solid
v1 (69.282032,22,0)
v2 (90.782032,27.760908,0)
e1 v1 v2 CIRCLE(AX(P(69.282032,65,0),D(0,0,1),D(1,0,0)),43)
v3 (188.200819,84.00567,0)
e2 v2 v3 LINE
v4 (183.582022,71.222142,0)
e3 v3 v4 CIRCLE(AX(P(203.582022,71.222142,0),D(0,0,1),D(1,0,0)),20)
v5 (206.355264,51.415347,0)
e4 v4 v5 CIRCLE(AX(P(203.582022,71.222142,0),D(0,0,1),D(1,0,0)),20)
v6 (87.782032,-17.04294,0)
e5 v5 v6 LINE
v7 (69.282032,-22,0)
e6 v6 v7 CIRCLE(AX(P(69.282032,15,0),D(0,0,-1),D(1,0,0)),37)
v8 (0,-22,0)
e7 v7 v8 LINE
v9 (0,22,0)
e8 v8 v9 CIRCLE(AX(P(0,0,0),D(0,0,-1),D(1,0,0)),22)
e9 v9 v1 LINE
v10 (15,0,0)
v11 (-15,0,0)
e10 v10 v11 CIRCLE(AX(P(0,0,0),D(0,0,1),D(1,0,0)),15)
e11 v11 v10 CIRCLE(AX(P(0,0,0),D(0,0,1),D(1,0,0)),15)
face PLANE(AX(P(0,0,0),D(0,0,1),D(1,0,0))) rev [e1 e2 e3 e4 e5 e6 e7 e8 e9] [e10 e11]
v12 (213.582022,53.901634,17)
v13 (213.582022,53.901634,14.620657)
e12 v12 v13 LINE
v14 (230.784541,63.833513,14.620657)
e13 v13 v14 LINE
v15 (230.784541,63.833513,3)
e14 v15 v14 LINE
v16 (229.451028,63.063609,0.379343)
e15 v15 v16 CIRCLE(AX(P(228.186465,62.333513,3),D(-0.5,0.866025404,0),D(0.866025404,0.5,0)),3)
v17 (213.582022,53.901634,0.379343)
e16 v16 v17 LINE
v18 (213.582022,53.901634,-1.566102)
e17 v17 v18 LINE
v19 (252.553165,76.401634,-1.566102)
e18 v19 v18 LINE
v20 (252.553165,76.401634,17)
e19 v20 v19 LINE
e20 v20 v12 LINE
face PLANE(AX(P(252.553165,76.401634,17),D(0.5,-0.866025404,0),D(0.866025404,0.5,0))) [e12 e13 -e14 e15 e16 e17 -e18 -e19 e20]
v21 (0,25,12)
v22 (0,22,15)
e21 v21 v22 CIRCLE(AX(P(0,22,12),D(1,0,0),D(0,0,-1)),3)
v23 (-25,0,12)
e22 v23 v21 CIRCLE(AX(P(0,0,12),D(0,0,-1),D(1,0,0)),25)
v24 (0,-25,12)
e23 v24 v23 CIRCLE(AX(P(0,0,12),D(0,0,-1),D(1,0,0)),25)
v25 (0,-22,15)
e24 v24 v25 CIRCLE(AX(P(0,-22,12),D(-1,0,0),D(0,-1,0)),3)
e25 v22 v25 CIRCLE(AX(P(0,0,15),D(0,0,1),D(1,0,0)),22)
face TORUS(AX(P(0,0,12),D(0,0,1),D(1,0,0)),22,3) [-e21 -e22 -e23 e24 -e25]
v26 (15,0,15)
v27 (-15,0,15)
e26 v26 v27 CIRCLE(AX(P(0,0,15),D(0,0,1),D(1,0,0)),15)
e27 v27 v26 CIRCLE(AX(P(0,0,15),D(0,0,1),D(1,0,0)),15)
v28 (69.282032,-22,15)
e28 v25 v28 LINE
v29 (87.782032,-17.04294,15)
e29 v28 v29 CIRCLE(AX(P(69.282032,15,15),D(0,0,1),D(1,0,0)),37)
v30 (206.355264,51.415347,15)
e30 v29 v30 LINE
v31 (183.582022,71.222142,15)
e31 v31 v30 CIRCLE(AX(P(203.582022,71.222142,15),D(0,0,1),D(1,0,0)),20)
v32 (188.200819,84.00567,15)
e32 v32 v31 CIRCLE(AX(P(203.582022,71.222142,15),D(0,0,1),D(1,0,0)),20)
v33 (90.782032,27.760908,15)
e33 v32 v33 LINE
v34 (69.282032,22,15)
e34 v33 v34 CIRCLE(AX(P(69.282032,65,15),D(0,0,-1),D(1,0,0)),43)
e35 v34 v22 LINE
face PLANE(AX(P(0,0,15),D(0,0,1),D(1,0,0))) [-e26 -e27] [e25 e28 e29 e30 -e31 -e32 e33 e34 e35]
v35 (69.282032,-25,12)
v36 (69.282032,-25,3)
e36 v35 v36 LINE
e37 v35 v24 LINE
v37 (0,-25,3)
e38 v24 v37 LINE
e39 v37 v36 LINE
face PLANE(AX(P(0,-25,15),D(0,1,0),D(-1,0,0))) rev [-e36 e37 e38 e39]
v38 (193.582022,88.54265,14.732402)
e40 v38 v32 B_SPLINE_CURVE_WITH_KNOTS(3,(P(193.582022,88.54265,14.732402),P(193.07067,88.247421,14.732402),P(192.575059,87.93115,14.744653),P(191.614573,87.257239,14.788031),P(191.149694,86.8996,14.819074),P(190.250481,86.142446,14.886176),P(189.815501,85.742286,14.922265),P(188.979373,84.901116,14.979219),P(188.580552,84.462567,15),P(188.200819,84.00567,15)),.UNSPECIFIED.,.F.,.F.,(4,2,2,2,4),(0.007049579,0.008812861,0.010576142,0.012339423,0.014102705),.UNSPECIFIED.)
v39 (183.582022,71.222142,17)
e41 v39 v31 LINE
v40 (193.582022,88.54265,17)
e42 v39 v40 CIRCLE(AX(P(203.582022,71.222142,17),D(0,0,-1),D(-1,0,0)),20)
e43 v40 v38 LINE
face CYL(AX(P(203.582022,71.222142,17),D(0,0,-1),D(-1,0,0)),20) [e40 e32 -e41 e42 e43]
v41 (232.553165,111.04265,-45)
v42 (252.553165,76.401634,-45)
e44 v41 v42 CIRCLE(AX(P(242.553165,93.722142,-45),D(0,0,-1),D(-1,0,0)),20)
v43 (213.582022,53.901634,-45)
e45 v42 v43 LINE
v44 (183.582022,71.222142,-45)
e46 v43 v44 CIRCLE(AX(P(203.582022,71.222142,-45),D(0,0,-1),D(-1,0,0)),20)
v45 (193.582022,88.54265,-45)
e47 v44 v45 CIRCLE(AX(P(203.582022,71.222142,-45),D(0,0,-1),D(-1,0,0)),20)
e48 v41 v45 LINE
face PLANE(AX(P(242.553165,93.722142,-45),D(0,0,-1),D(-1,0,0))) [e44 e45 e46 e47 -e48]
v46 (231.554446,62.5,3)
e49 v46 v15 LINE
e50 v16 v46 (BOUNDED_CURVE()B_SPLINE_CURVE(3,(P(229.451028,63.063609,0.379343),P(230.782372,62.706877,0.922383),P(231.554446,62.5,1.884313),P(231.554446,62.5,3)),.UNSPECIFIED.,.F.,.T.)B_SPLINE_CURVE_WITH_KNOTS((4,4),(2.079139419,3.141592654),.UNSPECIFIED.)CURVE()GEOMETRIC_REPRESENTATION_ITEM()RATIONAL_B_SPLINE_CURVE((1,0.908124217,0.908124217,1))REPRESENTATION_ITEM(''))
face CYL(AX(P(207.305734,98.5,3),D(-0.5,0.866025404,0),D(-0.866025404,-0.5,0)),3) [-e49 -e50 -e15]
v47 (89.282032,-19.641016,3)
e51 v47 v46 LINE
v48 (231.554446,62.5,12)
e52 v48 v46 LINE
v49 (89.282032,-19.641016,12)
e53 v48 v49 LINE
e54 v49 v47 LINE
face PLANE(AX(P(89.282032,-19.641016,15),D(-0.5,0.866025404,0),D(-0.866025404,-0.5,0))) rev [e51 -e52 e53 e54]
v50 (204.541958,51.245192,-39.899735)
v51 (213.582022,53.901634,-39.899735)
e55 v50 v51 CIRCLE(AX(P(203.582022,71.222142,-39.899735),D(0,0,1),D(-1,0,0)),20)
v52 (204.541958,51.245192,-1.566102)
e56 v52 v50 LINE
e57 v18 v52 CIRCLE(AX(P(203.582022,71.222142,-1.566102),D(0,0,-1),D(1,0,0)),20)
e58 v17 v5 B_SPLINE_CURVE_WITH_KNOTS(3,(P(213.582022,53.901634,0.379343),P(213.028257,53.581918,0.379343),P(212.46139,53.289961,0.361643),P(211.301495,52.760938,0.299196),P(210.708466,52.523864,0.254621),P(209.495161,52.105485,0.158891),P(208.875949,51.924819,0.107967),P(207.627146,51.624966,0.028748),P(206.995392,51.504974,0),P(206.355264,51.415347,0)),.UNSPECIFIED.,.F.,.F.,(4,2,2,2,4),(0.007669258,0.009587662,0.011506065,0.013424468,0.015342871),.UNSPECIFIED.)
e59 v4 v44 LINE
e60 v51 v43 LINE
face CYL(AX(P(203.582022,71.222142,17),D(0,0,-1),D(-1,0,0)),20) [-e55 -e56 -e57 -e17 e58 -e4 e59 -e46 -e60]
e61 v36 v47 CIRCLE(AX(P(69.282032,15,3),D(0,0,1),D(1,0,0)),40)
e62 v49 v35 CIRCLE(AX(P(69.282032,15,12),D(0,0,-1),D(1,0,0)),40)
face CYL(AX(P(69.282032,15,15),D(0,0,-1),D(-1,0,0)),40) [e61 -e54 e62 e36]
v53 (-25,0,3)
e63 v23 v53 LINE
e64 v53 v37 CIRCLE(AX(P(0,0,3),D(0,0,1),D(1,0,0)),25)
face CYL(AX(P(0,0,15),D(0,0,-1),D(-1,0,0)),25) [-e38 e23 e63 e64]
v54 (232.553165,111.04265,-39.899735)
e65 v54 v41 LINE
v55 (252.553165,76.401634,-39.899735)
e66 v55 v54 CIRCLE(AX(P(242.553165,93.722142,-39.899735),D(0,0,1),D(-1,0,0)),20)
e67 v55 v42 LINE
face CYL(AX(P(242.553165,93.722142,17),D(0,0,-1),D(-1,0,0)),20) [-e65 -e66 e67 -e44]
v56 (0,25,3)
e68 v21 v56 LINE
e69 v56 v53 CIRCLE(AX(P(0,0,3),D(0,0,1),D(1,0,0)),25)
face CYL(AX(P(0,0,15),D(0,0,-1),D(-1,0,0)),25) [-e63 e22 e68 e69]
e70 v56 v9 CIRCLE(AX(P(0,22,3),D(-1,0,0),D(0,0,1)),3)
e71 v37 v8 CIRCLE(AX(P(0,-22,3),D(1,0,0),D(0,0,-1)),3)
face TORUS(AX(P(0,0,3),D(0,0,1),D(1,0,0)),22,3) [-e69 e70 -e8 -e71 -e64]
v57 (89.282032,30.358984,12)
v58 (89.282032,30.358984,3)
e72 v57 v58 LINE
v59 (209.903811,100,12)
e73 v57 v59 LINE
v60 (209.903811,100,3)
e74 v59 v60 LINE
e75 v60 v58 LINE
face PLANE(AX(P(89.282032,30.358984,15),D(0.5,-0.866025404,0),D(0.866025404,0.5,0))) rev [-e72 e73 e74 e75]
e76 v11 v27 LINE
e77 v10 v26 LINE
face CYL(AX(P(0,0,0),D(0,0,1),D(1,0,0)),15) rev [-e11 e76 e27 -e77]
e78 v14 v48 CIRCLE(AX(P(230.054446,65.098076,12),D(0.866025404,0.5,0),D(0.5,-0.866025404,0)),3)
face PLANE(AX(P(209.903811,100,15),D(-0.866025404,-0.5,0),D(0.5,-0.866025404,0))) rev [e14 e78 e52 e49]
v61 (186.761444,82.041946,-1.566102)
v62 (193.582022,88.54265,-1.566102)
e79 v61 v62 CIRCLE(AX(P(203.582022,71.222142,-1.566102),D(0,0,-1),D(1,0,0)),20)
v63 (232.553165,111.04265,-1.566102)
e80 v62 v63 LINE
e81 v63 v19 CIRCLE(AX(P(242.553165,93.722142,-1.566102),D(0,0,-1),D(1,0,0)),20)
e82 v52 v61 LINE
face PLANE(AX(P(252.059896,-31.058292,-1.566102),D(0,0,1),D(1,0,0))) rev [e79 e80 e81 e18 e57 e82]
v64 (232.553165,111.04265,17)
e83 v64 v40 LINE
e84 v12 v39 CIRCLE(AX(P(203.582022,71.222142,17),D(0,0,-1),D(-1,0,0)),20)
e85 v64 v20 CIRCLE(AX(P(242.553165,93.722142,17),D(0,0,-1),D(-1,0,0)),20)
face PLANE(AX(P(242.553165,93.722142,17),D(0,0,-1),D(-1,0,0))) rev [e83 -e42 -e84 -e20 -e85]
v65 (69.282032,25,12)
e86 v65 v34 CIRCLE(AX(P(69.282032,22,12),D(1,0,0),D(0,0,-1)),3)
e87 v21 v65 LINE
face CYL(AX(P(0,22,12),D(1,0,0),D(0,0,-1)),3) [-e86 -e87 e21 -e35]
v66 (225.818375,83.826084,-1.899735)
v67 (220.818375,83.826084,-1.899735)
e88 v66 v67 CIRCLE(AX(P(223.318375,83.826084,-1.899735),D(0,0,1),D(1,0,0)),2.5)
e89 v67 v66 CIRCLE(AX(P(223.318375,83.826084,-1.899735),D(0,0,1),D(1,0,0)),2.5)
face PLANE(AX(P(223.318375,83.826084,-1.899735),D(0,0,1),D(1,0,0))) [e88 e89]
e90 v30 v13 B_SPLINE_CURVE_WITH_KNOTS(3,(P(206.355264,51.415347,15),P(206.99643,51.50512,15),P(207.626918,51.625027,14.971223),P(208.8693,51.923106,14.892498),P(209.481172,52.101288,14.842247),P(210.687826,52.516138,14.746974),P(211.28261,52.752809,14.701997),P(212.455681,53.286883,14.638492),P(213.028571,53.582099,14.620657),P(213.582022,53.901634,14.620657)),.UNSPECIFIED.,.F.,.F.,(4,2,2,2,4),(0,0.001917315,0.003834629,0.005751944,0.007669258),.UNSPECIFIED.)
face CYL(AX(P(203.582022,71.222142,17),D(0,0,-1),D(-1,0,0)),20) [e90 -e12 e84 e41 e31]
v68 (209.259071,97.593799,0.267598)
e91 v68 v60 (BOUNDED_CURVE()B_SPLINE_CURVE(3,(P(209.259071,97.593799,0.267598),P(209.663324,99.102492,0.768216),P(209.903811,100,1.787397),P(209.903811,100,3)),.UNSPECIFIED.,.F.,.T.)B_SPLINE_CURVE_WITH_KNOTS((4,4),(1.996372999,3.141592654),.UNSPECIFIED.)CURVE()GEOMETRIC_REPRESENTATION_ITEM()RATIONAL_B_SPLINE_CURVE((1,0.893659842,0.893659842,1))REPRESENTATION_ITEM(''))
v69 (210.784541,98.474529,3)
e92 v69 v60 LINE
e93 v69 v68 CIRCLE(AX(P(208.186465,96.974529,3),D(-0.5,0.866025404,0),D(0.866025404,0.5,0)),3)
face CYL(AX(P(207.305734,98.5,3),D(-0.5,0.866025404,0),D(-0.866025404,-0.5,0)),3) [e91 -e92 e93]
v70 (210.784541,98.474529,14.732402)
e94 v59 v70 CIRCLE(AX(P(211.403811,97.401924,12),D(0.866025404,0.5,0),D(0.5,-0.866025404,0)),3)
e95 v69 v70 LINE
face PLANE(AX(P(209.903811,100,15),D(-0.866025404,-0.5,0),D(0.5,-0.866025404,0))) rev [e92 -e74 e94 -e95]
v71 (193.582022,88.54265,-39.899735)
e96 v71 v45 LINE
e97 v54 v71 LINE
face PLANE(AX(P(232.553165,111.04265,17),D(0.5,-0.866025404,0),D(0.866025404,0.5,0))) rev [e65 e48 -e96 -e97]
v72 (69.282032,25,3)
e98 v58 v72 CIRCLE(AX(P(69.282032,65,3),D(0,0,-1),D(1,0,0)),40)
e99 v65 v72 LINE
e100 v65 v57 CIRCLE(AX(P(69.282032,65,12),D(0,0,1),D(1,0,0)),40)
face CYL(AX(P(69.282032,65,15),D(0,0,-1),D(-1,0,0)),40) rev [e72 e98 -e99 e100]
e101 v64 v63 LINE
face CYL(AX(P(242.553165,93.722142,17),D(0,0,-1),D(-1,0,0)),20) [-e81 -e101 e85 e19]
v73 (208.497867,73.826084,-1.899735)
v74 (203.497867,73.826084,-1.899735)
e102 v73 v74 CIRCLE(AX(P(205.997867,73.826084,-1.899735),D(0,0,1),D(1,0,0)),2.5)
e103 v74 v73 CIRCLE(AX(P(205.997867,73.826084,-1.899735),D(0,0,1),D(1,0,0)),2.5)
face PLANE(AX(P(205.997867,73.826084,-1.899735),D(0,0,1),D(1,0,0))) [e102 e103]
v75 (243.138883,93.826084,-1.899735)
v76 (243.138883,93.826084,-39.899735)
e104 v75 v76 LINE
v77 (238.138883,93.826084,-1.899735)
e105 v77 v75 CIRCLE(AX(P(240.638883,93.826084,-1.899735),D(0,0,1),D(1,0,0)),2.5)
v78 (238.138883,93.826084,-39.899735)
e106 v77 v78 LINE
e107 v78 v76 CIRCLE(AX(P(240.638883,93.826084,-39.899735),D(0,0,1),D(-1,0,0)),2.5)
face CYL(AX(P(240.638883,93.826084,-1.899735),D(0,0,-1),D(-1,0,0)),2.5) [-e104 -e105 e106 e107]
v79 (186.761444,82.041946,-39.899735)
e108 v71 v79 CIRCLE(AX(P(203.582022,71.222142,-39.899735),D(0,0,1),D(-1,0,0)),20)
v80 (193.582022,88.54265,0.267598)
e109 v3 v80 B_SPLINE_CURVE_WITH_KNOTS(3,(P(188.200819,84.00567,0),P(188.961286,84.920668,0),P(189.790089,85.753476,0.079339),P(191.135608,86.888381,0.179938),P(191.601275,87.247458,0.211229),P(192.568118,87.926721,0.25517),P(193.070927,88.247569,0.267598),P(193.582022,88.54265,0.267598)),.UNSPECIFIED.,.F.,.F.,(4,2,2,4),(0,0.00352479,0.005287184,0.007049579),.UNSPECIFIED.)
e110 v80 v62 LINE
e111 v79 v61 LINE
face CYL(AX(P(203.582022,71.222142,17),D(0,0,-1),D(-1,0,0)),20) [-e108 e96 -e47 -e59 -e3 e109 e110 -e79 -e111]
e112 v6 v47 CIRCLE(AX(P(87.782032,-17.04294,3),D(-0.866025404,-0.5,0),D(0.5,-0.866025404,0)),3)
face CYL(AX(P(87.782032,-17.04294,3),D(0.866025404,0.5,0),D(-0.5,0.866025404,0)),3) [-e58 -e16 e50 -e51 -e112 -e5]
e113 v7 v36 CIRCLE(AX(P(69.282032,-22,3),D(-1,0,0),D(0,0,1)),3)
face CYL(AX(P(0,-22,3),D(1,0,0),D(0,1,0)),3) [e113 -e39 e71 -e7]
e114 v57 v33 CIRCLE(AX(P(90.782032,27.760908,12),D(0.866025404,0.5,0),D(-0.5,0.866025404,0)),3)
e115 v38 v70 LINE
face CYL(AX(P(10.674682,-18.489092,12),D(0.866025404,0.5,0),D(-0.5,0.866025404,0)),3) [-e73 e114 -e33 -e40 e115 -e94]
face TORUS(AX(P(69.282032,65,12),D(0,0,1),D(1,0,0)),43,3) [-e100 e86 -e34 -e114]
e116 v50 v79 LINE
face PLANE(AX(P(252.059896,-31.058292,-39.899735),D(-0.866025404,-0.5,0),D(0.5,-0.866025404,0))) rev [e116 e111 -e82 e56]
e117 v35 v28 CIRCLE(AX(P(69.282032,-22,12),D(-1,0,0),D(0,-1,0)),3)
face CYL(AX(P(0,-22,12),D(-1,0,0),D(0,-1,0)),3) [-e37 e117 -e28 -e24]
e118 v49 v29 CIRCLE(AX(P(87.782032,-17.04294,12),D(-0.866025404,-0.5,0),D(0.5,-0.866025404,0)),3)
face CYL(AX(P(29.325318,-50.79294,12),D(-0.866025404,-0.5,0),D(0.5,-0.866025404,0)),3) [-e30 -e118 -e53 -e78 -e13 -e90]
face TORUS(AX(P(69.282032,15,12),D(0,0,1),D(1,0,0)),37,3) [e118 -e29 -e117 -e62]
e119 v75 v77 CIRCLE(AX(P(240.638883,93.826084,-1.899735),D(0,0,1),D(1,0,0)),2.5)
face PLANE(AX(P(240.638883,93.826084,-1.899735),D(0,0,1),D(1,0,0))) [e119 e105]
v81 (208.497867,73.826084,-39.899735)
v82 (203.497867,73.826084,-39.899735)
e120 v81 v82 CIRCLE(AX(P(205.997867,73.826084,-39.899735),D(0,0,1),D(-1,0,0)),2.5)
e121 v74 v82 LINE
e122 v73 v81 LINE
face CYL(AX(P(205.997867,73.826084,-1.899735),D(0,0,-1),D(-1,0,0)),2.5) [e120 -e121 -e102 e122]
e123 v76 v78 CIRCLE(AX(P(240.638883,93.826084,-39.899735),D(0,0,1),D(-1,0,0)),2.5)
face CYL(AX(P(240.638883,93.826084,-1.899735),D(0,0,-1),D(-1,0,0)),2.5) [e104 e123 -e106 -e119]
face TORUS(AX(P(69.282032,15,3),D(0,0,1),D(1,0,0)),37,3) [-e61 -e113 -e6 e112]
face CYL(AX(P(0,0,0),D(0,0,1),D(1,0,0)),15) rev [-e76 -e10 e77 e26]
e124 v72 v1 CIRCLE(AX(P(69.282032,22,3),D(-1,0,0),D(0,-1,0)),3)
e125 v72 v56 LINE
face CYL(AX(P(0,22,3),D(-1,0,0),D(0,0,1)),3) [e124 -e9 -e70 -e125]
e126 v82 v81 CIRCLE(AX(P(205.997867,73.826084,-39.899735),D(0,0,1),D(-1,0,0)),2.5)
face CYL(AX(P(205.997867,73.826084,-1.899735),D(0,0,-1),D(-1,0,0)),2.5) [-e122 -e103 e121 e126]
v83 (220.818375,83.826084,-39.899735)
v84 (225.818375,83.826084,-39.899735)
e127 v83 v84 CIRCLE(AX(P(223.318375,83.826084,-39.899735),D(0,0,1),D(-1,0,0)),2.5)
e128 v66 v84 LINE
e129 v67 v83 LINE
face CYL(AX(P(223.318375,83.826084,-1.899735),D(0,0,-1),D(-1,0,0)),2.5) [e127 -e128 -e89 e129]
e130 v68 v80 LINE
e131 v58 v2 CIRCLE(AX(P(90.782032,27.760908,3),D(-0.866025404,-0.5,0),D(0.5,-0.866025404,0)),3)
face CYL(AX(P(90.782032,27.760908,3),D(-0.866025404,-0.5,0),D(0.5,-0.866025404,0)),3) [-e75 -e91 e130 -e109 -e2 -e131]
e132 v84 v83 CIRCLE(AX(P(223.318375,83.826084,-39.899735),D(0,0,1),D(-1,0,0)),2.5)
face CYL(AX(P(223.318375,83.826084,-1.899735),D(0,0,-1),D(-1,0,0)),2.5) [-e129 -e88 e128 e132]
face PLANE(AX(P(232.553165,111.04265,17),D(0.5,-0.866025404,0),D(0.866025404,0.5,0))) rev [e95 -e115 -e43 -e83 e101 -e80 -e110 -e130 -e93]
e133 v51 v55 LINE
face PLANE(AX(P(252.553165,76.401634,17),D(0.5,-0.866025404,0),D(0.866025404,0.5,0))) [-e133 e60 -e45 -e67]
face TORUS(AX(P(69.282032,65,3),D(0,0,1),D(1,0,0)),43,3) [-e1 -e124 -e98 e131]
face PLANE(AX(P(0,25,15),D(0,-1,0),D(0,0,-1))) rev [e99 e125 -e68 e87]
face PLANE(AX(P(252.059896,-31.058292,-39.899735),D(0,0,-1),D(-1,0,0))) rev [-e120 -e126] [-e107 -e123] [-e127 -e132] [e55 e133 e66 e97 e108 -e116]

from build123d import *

# Parameters (mm, degrees)
BOSS_EXTRUDE1_DEPTH      = 15
FILLET1_R                = 3
SKETCH2_R                = 15
CUT_EXTRUDE1_DEPTH       = 253.670657786
BOSS_EXTRUDE2_DEPTH      = 45
BOSS_EXTRUDE2_DEPTH_BACK = 17
SKETCH6_W                = 83.616638364
SKETCH6_H                = 38.333633137
CUT_EXTRUDE3_DEPTH       = 289.058075248
SKETCH8_R                = 2.5
BOSS_EXTRUDE3_DEPTH      = 38
LPATTERN1_COUNT          = 3
LPATTERN1_PITCH          = 20


with BuildPart() as part:
    # Sketch1 → Boss-Extrude1 (new body)
    with BuildSketch(Plane.XY):
        with BuildLine():
            Line((0, 25), (69.282032303, 25))
            ThreePointArc((69.282032303, 25), (79.634794107, 26.362966948), (89.282032303, 30.358983849))
            Line((89.282032303, 30.358983849), (209.903810568, 100))
            Line((209.903810568, 100), (231.554445662, 62.5))
            Line((231.554445662, 62.5), (89.282032303, -19.641016151))
            ThreePointArc((89.282032303, -19.641016151), (79.634794107, -23.637033052), (69.282032303, -25))
            Line((69.282032303, -25), (0, -25))
            ThreePointArc((0, -25), (-25, 0), (0, 25))
        make_face()
    extrude(amount=BOSS_EXTRUDE1_DEPTH)

    # Fillet1
    fillet1_edges = [part.edges().sort_by_distance(p)[0] for p in [
        (160.418238983, 21.429491924, 0),
        (79.634794107, -23.637033052, 0),
        (34.641016151, -25, 0),
        (-25, 0, 0),
        (79.634794107, -23.637033052, 15),
        (160.418238983, 21.429491924, 15),
        (149.592921435, 65.179491924, 15),
        (79.634794107, 26.362966948, 15),
        (34.641016151, 25, 15),
        (-25, 0, 15),
        (34.641016151, 25, 0),
        (34.641016151, -25, 15),
        (79.634794107, 26.362966948, 0),
        (149.592921435, 65.179491924, 0),
        (220.729128115, 81.25, 0),
    ]]
    fillet(fillet1_edges, radius=FILLET1_R)

    # Sketch2 → Cut-Extrude1 (cut, through all)
    with BuildSketch(Plane.XY.offset(15)):
        Circle(SKETCH2_R)
    extrude(amount=-CUT_EXTRUDE1_DEPTH, mode=Mode.SUBTRACT)

    # Sketch3 → Boss-Extrude2 (add, two sides: drawn at the far end of the back side and taken through both)
    with BuildSketch(Plane(origin=(0, 0, 0), x_dir=(-1, 0, 0), z_dir=(0, 0, -1)).offset(-BOSS_EXTRUDE2_DEPTH_BACK)):
        with BuildLine():
            Line((-232.55316524, 111.042650187), (-193.582022069, 88.542650187))
            ThreePointArc((-193.582022069, 88.542650187), (-186.261513994, 61.222142112), (-213.582022069, 53.901634036))
            Line((-213.582022069, 53.901634036), (-252.55316524, 76.401634036))
            ThreePointArc((-252.55316524, 76.401634036), (-259.873673315, 103.722142112), (-232.55316524, 111.042650187))
        make_face()
    extrude(amount=BOSS_EXTRUDE2_DEPTH + BOSS_EXTRUDE2_DEPTH_BACK)

    # Sketch6 → Cut-Extrude3 (cut, through all)
    with BuildSketch(Plane(origin=(10.055413327, -17.416486774, 0), x_dir=(0.8660254037844389, 0.4999999999999995, 0), z_dir=(-0.4999999999999995, 0.8660254037844389, 0))):
        with Locations((244.569446826, 20.732918796)):
            Rectangle(SKETCH6_W, SKETCH6_H)
    extrude(amount=-CUT_EXTRUDE3_DEPTH, mode=Mode.SUBTRACT)

    # Sketch8 → Boss-Extrude3 (add)
    with BuildSketch(Plane.XY.offset(-39.899735364)):
        with Locations(Location((240.638883171, 93.826084401, 0), (0, 0, 180))):
            Circle(SKETCH8_R)
    boss_extrude3 = extrude(amount=BOSS_EXTRUDE3_DEPTH)

    # LPattern1: Boss-Extrude3 ×3
    with Locations(*[Vector(-0.8660254037844388, -0.49999999999999983, 0) * (i * LPATTERN1_PITCH) for i in range(1, LPATTERN1_COUNT)]):
        add(boss_extrude3)


solid = part.part
